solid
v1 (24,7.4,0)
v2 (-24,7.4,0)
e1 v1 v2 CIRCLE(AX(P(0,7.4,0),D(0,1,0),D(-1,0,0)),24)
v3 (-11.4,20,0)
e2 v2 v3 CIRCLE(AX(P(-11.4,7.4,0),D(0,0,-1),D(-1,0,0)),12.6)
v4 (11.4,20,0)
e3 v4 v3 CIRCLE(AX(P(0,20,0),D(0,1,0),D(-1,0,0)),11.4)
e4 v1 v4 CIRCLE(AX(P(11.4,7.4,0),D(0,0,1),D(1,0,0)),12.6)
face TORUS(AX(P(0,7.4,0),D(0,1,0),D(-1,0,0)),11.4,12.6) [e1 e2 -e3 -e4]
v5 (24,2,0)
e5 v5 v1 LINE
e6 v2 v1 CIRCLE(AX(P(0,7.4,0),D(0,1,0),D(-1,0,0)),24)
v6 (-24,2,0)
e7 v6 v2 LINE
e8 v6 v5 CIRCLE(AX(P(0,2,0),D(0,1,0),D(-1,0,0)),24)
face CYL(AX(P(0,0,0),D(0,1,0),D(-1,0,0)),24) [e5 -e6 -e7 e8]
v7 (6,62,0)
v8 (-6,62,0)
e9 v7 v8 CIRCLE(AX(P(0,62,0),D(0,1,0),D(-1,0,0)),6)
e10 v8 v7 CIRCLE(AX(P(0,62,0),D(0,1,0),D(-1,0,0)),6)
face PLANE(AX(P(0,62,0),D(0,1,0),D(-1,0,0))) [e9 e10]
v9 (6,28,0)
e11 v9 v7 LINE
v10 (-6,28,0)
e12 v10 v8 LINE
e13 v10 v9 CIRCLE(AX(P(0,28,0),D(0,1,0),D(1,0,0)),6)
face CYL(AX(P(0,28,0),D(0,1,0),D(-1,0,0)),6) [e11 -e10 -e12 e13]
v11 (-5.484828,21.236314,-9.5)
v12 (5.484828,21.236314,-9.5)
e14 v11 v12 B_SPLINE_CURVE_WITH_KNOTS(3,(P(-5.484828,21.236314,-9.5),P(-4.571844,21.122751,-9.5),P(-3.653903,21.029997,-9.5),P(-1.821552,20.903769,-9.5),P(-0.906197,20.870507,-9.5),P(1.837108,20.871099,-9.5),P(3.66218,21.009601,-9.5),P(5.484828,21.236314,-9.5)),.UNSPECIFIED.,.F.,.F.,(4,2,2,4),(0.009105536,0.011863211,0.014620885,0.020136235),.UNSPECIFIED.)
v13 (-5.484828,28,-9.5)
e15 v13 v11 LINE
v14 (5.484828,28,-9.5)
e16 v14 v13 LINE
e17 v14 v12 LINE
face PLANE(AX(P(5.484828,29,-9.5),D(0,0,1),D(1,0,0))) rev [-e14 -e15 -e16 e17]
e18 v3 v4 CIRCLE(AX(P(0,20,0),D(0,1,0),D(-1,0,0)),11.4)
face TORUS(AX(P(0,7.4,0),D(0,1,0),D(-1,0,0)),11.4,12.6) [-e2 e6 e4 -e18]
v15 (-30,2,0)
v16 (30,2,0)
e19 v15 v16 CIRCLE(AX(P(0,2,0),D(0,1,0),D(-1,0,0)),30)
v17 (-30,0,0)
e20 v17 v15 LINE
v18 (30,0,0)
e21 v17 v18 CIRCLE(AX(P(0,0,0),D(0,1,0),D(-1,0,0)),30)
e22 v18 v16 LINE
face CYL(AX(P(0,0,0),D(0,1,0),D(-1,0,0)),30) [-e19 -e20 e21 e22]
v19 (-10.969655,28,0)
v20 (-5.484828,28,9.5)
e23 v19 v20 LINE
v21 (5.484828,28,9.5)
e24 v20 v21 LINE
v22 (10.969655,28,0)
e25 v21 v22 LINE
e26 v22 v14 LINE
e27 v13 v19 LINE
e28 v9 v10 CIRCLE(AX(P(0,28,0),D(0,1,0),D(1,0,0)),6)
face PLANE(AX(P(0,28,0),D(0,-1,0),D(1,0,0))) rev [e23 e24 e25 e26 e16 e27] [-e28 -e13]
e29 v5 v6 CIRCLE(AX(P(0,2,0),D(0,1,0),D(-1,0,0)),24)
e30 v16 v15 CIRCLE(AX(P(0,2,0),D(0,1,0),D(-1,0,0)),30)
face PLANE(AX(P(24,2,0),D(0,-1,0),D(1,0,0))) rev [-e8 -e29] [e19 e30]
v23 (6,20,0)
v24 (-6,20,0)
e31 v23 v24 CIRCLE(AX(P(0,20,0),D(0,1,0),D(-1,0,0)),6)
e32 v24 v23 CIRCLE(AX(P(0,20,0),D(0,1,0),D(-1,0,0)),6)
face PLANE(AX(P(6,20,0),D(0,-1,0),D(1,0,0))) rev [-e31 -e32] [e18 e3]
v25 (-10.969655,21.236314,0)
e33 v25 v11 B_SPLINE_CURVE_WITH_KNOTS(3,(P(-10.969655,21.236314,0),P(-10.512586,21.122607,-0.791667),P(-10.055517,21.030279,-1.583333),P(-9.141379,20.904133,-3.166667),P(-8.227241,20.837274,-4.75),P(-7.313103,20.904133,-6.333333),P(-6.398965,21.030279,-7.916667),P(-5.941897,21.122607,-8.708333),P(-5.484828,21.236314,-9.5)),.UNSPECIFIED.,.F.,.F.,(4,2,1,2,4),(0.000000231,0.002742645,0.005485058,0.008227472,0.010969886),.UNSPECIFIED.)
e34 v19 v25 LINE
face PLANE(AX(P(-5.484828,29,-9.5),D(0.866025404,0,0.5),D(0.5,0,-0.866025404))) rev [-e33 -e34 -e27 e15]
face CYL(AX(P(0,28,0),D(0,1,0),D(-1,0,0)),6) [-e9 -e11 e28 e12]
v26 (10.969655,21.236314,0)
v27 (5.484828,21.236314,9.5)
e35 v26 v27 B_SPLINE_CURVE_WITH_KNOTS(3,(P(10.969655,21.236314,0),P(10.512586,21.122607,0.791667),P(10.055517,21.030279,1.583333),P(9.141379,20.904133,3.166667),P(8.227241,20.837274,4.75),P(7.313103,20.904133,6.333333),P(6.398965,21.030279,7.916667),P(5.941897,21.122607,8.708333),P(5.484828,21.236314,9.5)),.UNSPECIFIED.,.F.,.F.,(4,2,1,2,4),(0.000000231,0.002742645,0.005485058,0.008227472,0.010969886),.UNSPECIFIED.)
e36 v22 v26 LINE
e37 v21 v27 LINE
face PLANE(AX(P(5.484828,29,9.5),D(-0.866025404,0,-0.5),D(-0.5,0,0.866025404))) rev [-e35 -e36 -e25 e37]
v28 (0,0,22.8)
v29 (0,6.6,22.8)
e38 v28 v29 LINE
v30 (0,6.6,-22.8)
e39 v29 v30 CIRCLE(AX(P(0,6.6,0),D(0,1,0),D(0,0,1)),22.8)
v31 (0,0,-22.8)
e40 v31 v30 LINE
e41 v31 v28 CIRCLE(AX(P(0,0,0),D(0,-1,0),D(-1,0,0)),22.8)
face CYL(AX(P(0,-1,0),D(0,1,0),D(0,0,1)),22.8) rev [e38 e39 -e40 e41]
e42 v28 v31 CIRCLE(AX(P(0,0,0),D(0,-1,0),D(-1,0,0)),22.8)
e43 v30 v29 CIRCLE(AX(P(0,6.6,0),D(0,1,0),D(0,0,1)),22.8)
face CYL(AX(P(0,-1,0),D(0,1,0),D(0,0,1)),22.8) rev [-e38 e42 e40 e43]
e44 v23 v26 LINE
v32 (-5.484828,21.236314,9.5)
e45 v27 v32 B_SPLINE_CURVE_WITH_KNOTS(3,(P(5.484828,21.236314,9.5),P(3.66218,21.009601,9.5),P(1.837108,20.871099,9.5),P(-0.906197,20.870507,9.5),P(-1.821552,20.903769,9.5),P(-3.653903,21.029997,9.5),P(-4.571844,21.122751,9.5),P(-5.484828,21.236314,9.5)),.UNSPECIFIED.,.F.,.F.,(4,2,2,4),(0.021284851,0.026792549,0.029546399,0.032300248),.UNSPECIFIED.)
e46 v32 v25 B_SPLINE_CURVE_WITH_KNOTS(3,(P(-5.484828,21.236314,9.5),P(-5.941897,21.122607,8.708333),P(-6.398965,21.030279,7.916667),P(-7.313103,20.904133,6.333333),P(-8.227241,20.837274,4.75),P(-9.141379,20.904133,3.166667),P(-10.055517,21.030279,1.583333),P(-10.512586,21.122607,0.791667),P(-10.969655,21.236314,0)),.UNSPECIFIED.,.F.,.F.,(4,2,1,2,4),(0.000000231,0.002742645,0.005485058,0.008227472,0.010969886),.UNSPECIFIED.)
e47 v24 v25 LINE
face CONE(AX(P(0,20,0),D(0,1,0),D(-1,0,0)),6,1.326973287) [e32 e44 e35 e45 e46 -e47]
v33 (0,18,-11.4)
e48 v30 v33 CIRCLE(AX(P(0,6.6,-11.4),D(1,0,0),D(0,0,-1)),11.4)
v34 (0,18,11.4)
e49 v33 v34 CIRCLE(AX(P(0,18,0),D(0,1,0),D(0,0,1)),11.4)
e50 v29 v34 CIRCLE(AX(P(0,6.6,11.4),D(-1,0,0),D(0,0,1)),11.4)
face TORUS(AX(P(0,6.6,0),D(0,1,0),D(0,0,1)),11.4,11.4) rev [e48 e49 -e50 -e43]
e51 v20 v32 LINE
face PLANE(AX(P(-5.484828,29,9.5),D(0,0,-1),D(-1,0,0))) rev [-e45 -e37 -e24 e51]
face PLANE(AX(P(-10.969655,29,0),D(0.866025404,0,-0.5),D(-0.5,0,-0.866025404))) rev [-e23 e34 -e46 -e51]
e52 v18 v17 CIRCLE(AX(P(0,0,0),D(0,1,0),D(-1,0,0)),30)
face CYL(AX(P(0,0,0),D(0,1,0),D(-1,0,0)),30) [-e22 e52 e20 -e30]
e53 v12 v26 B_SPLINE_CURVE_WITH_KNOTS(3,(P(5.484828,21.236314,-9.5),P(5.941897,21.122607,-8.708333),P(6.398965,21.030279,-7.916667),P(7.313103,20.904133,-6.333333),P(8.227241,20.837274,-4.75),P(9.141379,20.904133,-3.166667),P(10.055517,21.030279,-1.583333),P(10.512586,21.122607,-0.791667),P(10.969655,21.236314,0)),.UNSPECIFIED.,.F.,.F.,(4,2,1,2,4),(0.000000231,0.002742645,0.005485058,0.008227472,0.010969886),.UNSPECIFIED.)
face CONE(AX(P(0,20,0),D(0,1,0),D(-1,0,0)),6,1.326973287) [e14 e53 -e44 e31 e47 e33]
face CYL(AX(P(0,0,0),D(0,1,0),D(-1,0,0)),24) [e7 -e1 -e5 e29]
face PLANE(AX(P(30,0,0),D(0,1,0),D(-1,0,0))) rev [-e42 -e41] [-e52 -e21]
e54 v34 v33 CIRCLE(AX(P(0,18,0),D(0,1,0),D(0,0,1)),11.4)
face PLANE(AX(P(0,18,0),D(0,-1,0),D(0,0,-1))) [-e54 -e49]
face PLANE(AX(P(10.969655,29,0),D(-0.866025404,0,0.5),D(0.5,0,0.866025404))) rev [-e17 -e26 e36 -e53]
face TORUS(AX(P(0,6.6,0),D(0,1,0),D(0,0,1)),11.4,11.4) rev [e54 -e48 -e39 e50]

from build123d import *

# Parameters (mm, degrees)
SKETCH3_R          = 12.35
CUT_EXTRUDE1_DEPTH = 9
SKETCH5_R          = 16.85236212
CUT_EXTRUDE2_DEPTH = 66


with BuildPart() as part:
    # Sketch1 → Revolve1 (revolve)
    with BuildSketch(Plane.XY, mode=Mode.PRIVATE) as revolve1_sk:
        with BuildLine():
            Line((0, 28), (11.875, 28))
            Line((11.875, 28), (11.875, 21.461538462))
            Line((11.875, 21.461538462), (6, 20))
            Line((6, 20), (11.4, 20))
            ThreePointArc((11.4, 20), (20.309545443, 16.309545443), (24, 7.4))
            Line((24, 7.4), (24, 2))
            Line((24, 2), (30, 2))
            Line((30, 2), (30, 0))
            Line((30, 0), (0, 0))
            Line((0, 0), (0, 28))
        make_face()
    revolve(revolve1_sk.sketch.rotate(Axis((0, 0, 0), (0, 1, 0)), 180), axis=Axis((0, 0, 0), (0, 1, 0)))

    # Sketch2 → Revolve2 (revolve)
    with BuildSketch(Plane.XY, mode=Mode.PRIVATE) as revolve2_sk:
        Polygon((0, 128), (4.9265, 128), (6, 126.9265), (6, 28), (0, 28), align=None)
    revolve(revolve2_sk.sketch.rotate(Axis((0, 28, 0), (0, 1, 0)), 180), axis=Axis((0, 28, 0), (0, 1, 0)))

    # Sketch3 → Cut-Extrude1 (cut)
    with BuildSketch(Plane(origin=(0, 20, 0), x_dir=(1, 0, 0), z_dir=(0, 1, 0))):
        Circle(SKETCH3_R)
        Polygon((-10.969655115, 0), (-5.484827557, -9.5), (5.484827557, -9.5), (10.969655115, 0), (5.484827557, 9.5), (-5.484827557, 9.5), align=None, mode=Mode.SUBTRACT)
    extrude(amount=CUT_EXTRUDE1_DEPTH, mode=Mode.SUBTRACT)

    # Sketch4 → Cut-Revolve1 (revolve, cut)
    with BuildSketch(Plane.XY, mode=Mode.PRIVATE) as cut_revolve1_sk:
        with BuildLine():
            Line((0, 18), (11.4, 18))
            ThreePointArc((11.4, 18), (19.461017306, 14.661017306), (22.8, 6.6))
            Line((22.8, 6.6), (22.8, -1))
            Line((22.8, -1), (0, -1))
            Line((0, -1), (0, 18))
        make_face()
    revolve(cut_revolve1_sk.sketch.rotate(Axis((0, -1, 0), (0, 1, 0)), 270), axis=Axis((0, -1, 0), (0, 1, 0)), mode=Mode.SUBTRACT)

    # Sketch5 → Cut-Extrude2 (cut)
    with BuildSketch(Plane(origin=(0, 128, 0), x_dir=(1, 0, 0), z_dir=(0, 1, 0))):
        Circle(SKETCH5_R)
    extrude(amount=-CUT_EXTRUDE2_DEPTH, mode=Mode.SUBTRACT)


solid = part.part
